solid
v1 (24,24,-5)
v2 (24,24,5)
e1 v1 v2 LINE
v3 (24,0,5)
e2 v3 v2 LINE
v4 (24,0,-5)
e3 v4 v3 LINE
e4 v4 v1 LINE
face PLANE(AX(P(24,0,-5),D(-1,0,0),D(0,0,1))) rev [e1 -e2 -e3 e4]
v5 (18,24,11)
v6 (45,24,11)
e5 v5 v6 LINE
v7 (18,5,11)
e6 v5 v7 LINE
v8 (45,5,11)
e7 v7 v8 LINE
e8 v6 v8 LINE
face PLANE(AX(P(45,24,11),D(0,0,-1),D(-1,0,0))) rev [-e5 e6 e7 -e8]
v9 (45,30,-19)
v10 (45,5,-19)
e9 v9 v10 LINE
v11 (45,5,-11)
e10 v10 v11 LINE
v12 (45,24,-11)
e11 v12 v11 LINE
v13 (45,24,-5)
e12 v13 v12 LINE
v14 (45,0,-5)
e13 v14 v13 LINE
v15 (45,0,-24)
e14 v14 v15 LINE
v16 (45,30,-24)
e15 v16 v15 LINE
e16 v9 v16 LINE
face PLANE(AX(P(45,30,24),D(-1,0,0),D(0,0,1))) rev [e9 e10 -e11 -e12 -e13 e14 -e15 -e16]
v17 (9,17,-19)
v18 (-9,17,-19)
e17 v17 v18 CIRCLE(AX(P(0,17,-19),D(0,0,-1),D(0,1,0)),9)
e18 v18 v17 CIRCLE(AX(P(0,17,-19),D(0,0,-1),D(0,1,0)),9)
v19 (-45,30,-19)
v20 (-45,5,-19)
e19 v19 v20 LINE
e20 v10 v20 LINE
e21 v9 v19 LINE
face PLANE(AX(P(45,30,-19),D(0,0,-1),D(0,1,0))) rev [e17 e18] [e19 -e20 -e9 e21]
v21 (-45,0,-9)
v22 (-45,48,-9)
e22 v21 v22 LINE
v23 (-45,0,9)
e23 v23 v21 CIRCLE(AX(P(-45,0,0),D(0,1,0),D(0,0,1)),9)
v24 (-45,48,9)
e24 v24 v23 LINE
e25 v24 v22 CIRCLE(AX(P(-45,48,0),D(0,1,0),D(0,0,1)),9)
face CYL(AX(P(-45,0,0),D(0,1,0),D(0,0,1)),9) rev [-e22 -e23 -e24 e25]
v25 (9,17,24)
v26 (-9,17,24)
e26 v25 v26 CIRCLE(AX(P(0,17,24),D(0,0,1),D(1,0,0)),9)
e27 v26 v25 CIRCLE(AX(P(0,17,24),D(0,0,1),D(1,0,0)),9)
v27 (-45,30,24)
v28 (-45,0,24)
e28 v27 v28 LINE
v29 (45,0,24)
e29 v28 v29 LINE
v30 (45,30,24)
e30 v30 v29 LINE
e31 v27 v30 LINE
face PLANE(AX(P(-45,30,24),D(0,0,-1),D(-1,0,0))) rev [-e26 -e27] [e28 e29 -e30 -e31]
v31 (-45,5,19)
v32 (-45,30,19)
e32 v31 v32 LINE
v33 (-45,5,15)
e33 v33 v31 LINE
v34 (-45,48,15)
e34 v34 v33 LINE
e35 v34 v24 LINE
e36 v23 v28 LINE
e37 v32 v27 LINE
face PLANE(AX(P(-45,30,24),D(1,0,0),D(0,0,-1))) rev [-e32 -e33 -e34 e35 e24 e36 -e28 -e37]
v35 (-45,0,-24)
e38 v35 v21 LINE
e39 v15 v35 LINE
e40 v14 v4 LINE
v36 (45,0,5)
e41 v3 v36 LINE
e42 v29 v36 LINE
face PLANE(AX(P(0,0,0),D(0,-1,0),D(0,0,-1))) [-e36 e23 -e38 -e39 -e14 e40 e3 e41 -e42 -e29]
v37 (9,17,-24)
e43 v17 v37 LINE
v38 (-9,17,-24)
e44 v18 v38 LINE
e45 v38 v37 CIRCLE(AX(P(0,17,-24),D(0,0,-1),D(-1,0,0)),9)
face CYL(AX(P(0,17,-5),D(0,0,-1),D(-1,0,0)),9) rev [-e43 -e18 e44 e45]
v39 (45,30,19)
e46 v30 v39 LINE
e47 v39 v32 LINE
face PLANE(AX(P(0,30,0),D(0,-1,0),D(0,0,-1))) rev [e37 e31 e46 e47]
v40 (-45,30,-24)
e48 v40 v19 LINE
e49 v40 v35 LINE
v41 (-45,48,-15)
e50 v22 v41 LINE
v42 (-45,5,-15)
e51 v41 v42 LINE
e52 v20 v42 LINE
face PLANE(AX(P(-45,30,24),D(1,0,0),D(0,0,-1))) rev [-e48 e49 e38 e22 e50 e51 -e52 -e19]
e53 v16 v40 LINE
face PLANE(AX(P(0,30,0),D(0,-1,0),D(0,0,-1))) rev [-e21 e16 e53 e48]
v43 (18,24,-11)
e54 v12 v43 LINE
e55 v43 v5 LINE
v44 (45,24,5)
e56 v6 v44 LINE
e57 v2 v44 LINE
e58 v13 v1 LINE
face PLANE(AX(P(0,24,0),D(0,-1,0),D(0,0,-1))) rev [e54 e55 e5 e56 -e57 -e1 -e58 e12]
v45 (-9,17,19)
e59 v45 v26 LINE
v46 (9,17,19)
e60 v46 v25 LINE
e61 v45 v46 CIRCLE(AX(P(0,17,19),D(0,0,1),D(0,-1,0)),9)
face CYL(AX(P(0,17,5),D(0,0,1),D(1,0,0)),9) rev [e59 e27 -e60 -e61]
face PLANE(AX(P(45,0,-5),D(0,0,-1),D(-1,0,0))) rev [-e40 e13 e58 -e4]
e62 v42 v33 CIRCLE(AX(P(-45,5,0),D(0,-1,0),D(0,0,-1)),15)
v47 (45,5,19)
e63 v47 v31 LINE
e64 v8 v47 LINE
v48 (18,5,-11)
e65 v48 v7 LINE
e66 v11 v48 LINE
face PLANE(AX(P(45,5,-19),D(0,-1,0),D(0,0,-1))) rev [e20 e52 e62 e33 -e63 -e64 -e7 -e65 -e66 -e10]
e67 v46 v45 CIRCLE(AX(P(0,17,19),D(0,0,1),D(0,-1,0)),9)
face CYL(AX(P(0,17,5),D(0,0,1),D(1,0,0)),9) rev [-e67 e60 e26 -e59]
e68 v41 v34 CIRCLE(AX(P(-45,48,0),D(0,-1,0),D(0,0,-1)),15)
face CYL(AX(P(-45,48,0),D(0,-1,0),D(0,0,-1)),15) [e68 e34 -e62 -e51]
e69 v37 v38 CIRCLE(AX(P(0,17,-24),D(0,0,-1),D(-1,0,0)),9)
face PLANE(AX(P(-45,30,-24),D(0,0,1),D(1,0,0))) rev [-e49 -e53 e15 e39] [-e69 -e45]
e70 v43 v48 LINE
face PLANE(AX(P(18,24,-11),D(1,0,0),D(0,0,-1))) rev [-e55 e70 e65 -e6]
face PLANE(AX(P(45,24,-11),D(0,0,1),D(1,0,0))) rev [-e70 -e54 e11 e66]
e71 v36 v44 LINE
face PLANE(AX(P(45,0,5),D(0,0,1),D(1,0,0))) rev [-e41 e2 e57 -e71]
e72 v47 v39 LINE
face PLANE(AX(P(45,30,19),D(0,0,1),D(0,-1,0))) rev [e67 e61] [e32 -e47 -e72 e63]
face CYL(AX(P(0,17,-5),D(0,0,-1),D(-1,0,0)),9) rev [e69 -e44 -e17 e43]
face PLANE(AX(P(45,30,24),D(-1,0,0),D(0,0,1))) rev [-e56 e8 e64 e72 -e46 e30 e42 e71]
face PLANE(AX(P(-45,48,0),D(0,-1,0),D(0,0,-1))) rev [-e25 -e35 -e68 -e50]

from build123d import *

# Parameters (mm, degrees)
BASE_BLOCK_SKETCH_W         = 90
BASE_BLOCK_SKETCH_H         = 48
BASE_BLOCK_90X48X30_DEPTH   = 30
CHANNEL_SKETCH_W            = 38
CHANNEL_SKETCH_H            = 25
U_CHANNEL_CUT_DEPTH         = 98.857038582
HALF_CYLINDER_POST_30_DEPTH = 48
POST_BORE_SKETCH_R          = 9
POST_BORE_18_DEPTH          = 48
END_TAB_SKETCH_W            = 27
END_TAB_SKETCH_H            = 22
END_TAB_DEPTH               = 19
END_TAB_SLOT_SKETCH_W       = 21
END_TAB_SLOT_SKETCH_H       = 10
END_TAB_SLOT_DEPTH          = 57.364882684
SIDE_HOLE_SKETCH_R          = 9
SIDE_HOLE_18_DEPTH          = 19
OPPOSITE_START              = -19
OPPOSITE_SIDE_HOLE_SKETCH_R = 9
OPPOSITE_SIDE_HOLE_18_DEPTH = 19


with BuildPart() as part:
    # Base Block Sketch → Base Block 90x48x30 (new body)
    with BuildSketch(Plane(origin=(0, 0, 0), x_dir=(1, 0, 0), z_dir=(0, 1, 0))):
        Rectangle(BASE_BLOCK_SKETCH_W, BASE_BLOCK_SKETCH_H)
    extrude(amount=BASE_BLOCK_90X48X30_DEPTH)

    # Channel Sketch → U-Channel Cut (cut, through all)
    with BuildSketch(Plane.ZY.offset(45)):
        with Locations((0, 17.5)):
            Rectangle(CHANNEL_SKETCH_W, CHANNEL_SKETCH_H)
    extrude(amount=-U_CHANNEL_CUT_DEPTH, mode=Mode.SUBTRACT)

    # Half Cylinder Post Sketch → Half Cylinder Post Ø30 (add)
    with BuildSketch(Plane.XZ):
        with BuildLine():
            Line((-45, 15), (-45, -15))
            ThreePointArc((-45, -15), (-30, 0), (-45, 15))
        make_face()
    extrude(amount=-HALF_CYLINDER_POST_30_DEPTH)

    # Post Bore Sketch → Post Bore Ø18 (cut)
    with BuildSketch(Plane(origin=(0, 48, 0), x_dir=(1, 0, 0), z_dir=(0, 1, 0))):
        with Locations((-45, 0)):
            Circle(POST_BORE_SKETCH_R)
    extrude(amount=-POST_BORE_18_DEPTH, mode=Mode.SUBTRACT)

    # End Tab Sketch → End Tab (add)
    with BuildSketch(Plane(origin=(0, 5, 0), x_dir=(1, 0, 0), z_dir=(0, 1, 0))):
        with Locations((31.5, 0)):
            Rectangle(END_TAB_SKETCH_W, END_TAB_SKETCH_H)
    extrude(amount=END_TAB_DEPTH)

    # End Tab Slot Sketch → End Tab Slot (cut, through all)
    with BuildSketch(Plane(origin=(0, 24, 0), x_dir=(1, 0, 0), z_dir=(0, 1, 0))):
        with Locations((34.5, 0)):
            Rectangle(END_TAB_SLOT_SKETCH_W, END_TAB_SLOT_SKETCH_H)
    extrude(amount=-END_TAB_SLOT_DEPTH, mode=Mode.SUBTRACT)

    # Side Hole Sketch → Side Hole Ø18 (cut)
    with BuildSketch(Plane.XY.offset(24)):
        with Locations((0, 17)):
            Circle(SIDE_HOLE_SKETCH_R)
    extrude(amount=-SIDE_HOLE_18_DEPTH, mode=Mode.SUBTRACT)

    # Opposite Side Hole Sketch → Opposite Side Hole Ø18 (cut)
    with BuildSketch(Plane(origin=(0, 0, -24), x_dir=(-1, 0, 0), z_dir=(0, 0, -1)).offset(OPPOSITE_START)):
        with Locations(Location((0, 17, 0), (0, 0, 180))):
            Circle(OPPOSITE_SIDE_HOLE_SKETCH_R)
    extrude(amount=OPPOSITE_SIDE_HOLE_18_DEPTH, mode=Mode.SUBTRACT)


solid = part.part
